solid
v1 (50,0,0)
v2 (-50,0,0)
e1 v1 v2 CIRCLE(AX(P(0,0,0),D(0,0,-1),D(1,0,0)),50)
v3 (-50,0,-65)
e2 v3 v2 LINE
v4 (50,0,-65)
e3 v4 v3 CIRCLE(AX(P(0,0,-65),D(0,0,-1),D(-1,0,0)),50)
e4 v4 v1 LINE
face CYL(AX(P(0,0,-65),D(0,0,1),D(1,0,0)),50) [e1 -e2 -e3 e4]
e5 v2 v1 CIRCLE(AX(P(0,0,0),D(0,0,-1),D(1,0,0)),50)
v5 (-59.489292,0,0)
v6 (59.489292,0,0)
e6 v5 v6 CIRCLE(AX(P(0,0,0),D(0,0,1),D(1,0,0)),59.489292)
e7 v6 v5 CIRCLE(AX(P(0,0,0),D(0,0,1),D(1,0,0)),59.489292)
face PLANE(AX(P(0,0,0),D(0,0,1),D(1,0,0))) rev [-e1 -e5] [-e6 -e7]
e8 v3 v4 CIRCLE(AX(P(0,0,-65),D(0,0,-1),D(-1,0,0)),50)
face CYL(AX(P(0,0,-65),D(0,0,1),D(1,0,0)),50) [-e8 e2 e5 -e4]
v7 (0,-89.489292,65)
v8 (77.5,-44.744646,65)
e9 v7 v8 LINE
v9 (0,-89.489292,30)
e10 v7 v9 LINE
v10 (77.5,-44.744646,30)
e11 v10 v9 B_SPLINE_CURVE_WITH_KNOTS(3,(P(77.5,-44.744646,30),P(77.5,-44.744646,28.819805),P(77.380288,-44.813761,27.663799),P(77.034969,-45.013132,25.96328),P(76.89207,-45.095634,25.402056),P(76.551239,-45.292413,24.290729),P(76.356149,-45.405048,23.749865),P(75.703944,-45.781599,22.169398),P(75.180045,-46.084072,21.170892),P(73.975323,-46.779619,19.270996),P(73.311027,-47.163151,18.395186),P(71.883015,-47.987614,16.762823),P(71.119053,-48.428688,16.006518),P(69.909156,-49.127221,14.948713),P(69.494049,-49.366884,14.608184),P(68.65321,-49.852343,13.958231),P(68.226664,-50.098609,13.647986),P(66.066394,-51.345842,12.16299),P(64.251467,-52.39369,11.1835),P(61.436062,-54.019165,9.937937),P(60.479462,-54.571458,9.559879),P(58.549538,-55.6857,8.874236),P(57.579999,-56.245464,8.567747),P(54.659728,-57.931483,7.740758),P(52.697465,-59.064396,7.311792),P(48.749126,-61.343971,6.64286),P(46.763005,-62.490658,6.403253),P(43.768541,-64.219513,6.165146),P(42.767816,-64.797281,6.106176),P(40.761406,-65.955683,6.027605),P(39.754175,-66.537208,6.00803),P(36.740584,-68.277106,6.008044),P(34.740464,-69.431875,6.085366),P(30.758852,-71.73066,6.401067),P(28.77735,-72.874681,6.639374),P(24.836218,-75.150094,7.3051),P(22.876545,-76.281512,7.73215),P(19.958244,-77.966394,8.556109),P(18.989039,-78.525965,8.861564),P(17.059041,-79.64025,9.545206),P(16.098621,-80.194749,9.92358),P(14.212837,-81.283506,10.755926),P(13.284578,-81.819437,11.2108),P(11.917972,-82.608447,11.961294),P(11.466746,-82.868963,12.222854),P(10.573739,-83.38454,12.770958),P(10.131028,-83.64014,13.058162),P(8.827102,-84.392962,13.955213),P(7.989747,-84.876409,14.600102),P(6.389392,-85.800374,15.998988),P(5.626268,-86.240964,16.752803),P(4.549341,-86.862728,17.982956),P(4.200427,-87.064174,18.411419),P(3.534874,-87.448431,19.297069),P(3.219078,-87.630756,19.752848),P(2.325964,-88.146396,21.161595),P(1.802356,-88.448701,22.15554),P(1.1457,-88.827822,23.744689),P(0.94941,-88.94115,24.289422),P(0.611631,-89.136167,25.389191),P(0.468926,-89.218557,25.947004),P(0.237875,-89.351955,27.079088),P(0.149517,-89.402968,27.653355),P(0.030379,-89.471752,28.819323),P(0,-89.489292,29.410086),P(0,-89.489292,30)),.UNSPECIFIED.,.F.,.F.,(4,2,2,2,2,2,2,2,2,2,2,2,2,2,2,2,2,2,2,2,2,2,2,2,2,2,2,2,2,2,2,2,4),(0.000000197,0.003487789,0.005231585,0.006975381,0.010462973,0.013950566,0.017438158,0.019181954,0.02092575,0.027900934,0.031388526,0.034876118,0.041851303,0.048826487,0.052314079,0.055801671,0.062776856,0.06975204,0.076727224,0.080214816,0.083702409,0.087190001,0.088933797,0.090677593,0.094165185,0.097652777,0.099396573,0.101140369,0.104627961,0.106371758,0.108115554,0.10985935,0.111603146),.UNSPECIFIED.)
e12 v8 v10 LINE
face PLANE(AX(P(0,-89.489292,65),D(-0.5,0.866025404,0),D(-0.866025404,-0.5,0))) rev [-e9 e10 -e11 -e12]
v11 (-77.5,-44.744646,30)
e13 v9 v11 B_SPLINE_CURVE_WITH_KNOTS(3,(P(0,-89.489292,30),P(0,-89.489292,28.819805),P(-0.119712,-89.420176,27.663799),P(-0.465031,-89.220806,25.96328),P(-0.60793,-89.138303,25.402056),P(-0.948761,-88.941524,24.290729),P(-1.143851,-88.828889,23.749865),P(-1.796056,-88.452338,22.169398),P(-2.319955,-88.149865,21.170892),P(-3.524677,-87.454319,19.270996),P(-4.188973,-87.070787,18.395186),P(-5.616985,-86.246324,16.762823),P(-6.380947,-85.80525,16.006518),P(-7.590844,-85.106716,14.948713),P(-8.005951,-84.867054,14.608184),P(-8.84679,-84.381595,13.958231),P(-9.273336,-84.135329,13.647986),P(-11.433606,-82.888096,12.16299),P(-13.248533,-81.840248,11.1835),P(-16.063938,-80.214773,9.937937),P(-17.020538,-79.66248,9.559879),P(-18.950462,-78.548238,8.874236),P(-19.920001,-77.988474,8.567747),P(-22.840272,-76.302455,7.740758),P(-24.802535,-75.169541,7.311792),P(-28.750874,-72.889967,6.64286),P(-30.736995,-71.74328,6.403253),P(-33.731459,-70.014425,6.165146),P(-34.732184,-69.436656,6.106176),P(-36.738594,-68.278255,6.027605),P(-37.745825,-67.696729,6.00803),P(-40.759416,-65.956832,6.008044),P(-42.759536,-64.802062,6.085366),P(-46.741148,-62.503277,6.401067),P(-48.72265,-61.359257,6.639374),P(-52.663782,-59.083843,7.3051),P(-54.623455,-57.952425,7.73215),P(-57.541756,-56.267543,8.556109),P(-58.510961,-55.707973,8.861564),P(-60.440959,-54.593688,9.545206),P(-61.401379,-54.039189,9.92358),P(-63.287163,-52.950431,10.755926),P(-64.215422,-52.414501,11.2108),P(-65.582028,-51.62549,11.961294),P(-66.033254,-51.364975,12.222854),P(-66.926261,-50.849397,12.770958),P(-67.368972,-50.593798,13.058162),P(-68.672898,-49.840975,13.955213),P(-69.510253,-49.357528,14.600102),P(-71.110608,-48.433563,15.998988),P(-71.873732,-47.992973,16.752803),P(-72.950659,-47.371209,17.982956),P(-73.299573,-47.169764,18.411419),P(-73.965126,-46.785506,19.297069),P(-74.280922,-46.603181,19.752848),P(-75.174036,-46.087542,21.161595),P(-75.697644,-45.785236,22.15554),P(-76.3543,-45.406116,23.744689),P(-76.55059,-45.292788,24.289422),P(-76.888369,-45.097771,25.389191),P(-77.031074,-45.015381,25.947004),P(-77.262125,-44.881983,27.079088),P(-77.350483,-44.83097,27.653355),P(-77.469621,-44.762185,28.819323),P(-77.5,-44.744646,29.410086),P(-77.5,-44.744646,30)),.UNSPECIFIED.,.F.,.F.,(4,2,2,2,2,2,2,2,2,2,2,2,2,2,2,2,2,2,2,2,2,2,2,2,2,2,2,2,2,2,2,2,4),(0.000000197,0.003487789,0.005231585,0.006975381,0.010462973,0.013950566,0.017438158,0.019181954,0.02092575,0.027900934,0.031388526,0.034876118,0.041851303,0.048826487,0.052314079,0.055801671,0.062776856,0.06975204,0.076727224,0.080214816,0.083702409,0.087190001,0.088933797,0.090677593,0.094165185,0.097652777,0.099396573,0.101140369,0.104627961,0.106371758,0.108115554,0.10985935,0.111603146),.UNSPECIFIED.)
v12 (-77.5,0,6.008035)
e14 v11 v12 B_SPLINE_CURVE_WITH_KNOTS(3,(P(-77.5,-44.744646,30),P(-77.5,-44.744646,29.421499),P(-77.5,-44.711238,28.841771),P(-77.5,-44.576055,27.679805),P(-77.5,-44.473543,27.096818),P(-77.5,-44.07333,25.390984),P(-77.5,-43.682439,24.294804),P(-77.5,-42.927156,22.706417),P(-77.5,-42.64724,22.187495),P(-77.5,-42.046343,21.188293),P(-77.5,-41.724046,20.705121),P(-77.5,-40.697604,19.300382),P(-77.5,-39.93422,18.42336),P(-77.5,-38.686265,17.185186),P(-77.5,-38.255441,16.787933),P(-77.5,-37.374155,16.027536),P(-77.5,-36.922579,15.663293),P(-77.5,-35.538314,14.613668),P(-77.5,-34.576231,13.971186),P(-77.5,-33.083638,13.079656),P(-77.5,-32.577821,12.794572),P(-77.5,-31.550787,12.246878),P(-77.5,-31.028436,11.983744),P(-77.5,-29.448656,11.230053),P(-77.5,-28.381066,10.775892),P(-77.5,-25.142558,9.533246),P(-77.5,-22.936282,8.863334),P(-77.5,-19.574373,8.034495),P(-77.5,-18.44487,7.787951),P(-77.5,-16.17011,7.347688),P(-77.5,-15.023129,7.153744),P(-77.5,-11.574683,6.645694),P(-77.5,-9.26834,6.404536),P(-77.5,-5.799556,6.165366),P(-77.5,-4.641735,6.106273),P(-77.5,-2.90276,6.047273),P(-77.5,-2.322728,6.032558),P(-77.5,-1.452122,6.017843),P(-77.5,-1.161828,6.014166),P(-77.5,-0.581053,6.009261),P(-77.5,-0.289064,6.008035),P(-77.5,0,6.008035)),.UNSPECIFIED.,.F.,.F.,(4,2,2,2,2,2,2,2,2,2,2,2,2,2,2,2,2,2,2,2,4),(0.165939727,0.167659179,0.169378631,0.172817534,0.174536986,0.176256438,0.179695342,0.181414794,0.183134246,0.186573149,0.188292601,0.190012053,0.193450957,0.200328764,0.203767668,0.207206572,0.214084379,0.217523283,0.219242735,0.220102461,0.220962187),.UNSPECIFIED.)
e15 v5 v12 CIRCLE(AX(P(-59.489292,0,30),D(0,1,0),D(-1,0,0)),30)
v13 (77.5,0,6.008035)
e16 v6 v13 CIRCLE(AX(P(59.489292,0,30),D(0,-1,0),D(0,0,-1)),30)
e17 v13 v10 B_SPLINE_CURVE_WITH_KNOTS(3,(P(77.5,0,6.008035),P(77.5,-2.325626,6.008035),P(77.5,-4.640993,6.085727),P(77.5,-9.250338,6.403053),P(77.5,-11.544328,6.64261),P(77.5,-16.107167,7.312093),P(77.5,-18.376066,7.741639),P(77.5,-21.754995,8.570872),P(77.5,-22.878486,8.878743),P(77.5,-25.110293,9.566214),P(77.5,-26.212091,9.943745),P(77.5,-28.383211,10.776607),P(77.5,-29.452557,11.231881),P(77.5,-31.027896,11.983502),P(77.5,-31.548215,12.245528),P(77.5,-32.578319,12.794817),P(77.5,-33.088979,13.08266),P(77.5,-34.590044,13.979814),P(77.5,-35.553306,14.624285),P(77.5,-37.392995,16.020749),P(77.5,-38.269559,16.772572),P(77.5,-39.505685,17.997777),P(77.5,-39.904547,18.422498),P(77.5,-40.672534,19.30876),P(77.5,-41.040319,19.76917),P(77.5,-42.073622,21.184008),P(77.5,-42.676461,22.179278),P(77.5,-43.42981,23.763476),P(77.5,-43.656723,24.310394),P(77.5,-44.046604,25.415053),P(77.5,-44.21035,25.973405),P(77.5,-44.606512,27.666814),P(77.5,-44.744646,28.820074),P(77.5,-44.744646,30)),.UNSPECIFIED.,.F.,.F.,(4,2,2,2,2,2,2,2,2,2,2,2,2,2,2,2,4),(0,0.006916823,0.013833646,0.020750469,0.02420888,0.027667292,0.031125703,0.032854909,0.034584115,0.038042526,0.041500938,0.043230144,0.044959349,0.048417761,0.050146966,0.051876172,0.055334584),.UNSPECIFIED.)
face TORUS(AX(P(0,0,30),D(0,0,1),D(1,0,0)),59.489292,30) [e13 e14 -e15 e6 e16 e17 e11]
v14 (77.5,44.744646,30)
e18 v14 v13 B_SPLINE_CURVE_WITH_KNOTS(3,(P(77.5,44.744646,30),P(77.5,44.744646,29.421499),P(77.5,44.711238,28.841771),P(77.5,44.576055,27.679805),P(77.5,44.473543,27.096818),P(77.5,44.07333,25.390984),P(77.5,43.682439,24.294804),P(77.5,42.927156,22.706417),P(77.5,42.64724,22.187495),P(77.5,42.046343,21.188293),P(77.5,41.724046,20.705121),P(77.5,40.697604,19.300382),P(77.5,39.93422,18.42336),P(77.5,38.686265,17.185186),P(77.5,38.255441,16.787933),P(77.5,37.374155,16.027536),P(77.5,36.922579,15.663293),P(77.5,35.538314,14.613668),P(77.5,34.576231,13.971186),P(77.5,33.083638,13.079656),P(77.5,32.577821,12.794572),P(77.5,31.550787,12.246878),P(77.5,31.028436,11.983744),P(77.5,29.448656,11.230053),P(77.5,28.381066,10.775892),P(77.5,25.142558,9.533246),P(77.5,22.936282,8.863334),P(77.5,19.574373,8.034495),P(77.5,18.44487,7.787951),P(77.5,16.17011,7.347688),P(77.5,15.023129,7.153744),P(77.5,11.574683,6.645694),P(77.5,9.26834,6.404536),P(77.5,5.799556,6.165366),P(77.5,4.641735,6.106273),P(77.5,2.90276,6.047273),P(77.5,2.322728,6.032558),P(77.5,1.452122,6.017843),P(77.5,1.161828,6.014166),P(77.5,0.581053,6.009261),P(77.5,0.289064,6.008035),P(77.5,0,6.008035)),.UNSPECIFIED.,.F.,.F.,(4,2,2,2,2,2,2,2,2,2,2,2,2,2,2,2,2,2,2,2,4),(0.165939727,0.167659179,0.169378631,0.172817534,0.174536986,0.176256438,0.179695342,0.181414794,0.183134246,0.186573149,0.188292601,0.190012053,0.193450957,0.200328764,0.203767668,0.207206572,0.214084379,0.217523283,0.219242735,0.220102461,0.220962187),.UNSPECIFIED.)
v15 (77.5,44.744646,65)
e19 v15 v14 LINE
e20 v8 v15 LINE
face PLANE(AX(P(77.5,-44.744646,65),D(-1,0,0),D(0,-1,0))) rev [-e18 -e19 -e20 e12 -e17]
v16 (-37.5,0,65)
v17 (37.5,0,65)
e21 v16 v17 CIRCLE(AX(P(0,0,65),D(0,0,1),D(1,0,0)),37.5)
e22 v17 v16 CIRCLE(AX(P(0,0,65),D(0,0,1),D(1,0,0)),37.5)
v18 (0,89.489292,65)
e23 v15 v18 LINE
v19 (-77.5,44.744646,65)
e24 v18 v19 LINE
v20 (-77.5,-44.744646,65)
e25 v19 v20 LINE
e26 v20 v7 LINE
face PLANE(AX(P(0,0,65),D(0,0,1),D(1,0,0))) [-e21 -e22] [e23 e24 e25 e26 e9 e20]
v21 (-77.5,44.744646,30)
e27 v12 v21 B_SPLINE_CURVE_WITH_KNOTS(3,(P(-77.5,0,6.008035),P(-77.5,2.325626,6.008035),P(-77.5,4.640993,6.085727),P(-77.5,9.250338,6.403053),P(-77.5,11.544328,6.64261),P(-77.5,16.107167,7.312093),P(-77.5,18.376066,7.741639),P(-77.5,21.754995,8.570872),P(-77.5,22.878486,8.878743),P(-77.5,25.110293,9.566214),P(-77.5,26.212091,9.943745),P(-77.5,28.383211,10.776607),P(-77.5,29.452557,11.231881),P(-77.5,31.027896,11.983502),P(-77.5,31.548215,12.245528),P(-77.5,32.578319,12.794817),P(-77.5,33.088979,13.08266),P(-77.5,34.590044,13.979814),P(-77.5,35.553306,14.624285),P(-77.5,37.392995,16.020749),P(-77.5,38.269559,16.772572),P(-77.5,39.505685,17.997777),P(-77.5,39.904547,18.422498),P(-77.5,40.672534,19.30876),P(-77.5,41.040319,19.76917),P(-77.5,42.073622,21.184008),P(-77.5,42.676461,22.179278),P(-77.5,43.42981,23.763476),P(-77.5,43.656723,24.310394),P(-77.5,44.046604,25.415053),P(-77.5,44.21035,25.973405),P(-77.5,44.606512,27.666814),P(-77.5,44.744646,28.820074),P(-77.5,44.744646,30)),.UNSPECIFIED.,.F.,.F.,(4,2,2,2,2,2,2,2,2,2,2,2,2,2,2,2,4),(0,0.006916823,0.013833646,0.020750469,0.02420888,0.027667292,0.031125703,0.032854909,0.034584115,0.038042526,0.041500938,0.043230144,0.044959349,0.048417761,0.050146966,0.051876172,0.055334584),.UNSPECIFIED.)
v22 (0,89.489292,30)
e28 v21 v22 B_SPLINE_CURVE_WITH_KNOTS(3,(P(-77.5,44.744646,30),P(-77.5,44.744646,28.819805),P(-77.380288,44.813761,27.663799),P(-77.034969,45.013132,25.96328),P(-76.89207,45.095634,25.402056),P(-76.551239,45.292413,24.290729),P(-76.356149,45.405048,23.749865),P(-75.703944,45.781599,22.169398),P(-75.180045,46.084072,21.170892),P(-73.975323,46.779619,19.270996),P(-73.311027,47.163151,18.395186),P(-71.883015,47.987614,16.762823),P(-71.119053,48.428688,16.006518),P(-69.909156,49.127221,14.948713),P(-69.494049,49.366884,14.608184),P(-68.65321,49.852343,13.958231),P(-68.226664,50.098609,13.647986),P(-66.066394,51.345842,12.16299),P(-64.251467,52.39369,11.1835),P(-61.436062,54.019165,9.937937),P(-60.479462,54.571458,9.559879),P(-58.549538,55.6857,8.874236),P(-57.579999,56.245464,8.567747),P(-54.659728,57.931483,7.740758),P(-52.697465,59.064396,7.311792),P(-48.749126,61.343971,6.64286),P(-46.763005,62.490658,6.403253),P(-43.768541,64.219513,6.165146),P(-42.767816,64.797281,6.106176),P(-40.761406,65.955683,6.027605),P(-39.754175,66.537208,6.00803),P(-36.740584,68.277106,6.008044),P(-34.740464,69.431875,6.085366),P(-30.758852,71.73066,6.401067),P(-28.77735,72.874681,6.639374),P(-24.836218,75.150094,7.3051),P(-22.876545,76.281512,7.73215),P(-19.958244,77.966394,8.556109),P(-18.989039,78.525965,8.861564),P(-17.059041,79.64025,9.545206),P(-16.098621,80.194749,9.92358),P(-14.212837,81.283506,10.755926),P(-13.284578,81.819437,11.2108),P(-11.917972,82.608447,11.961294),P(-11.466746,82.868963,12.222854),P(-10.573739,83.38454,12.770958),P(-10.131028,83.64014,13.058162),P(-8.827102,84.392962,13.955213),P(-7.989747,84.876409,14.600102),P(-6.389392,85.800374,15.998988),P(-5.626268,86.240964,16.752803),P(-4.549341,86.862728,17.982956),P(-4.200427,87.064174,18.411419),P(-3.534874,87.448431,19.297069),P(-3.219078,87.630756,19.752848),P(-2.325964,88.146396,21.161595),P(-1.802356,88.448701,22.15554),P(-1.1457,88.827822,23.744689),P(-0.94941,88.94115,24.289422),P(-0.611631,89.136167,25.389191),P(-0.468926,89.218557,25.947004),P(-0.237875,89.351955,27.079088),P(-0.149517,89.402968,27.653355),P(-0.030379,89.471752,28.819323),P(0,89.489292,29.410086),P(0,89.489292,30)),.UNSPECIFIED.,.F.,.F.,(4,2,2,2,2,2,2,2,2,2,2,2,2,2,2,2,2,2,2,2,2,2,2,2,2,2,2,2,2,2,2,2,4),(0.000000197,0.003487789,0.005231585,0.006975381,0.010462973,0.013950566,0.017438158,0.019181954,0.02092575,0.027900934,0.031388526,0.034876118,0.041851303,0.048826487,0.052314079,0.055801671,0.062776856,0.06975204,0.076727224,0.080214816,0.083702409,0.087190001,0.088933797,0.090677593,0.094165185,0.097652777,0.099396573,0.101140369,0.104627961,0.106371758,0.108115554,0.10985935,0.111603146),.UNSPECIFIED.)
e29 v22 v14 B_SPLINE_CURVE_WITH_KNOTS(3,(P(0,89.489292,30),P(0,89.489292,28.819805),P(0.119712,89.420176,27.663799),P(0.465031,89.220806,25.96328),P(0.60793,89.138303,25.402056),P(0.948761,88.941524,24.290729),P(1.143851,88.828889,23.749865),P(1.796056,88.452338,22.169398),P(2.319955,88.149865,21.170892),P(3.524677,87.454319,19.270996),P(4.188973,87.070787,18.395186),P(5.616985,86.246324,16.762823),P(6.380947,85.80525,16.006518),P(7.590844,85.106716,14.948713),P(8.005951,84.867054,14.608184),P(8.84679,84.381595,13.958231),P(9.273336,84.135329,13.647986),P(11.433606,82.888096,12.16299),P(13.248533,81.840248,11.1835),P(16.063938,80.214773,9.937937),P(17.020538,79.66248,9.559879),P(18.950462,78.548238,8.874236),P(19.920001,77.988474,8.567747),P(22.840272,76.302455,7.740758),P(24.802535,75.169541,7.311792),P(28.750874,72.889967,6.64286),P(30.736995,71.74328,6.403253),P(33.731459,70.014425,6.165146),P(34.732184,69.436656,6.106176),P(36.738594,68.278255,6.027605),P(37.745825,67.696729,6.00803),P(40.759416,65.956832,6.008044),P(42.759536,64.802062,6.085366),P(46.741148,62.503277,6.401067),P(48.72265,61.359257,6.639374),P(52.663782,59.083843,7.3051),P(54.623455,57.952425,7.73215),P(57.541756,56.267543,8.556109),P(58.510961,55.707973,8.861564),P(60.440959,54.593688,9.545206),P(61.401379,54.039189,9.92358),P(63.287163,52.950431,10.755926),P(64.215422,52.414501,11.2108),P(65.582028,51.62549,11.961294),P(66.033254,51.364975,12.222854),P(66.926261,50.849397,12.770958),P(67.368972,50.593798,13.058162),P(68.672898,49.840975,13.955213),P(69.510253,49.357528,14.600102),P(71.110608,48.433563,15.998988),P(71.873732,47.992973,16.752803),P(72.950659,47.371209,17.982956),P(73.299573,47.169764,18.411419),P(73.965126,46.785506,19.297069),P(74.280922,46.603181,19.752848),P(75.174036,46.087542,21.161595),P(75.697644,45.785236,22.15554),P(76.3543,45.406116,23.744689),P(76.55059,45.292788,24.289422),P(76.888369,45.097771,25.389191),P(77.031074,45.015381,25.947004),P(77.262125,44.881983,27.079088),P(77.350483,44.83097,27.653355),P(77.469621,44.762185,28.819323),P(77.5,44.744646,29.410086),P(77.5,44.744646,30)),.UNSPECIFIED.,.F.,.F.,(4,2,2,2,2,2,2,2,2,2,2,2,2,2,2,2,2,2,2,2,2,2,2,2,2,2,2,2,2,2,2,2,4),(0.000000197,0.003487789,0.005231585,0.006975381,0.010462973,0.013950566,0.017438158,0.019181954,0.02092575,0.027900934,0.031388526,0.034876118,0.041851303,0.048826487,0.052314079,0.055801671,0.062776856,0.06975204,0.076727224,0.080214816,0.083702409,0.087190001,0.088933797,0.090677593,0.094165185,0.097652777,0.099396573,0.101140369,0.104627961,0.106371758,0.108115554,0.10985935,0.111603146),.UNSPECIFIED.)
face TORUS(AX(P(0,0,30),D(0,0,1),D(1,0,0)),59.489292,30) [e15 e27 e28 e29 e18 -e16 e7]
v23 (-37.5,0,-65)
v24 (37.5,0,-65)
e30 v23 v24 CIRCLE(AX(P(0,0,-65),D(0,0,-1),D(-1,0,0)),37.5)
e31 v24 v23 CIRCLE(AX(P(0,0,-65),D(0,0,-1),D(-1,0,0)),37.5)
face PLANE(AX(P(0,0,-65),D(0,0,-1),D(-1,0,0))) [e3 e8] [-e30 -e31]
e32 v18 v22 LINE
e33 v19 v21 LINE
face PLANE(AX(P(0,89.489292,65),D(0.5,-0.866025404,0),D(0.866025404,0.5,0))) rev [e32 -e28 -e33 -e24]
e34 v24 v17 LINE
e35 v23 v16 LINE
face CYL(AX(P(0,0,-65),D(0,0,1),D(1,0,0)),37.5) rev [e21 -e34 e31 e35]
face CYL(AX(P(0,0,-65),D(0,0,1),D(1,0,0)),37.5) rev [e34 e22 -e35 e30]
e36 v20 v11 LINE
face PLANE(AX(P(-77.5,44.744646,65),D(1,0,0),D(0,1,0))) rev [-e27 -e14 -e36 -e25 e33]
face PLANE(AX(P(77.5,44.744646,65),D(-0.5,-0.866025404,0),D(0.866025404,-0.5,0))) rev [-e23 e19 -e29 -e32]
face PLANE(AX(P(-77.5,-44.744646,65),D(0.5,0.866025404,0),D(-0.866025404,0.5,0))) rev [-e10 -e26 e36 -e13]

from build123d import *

# Parameters (mm, degrees)
BOSS_EXTRUDE1_DEPTH = 65
SKETCH3_R           = 50
SKETCH3_R_2         = 37.5
BOSS_EXTRUDE2_DEPTH = 65
SKETCH4_R           = 37.5
CUT_EXTRUDE2_DEPTH  = 130


with BuildPart() as part:
    # Sketch1 → Boss-Extrude1 (new body)
    with BuildSketch(Plane.XY):
        Polygon((77.5, 44.744645862), (0, 89.489291724), (-77.5, 44.744645862), (-77.5, -44.744645862), (0, -89.489291724), (77.5, -44.744645862), align=None)
    extrude(amount=BOSS_EXTRUDE1_DEPTH)

    # Sketch2 → Cut-Revolve1 (revolve, cut)
    with BuildSketch(Plane(origin=(0, 0, 0), x_dir=(0, 0, -1), z_dir=(1, 0, 0)), mode=Mode.PRIVATE) as cut_revolve1_sk:
        with BuildLine():
            Line((0, 59.489291724), (0, 89.489291724))
            Line((0, 89.489291724), (-30, 89.489291724))
            ThreePointArc((-30, 89.489291724), (-8.786796564, 80.70249516), (0, 59.489291724))
        make_face()
    revolve(cut_revolve1_sk.sketch.rotate(Axis((0, 0, 90.10395437), (0, 0, -1)), 90), axis=Axis((0, 0, 90.10395437), (0, 0, -1)), mode=Mode.SUBTRACT)

    # Sketch3 → Boss-Extrude2 (add)
    with BuildSketch(Plane(origin=(0, 0, 0), x_dir=(-1, 0, 0), z_dir=(0, 0, -1))):
        with Locations(Location((0, 0, 0), (0, 0, 180))):
            Circle(SKETCH3_R)
        Circle(SKETCH3_R_2, mode=Mode.SUBTRACT)
    extrude(amount=BOSS_EXTRUDE2_DEPTH)

    # Sketch4 → Cut-Extrude2 (cut)
    with BuildSketch(Plane.XY.offset(65)):
        Circle(SKETCH4_R)
    extrude(amount=-CUT_EXTRUDE2_DEPTH, mode=Mode.SUBTRACT)


solid = part.part
